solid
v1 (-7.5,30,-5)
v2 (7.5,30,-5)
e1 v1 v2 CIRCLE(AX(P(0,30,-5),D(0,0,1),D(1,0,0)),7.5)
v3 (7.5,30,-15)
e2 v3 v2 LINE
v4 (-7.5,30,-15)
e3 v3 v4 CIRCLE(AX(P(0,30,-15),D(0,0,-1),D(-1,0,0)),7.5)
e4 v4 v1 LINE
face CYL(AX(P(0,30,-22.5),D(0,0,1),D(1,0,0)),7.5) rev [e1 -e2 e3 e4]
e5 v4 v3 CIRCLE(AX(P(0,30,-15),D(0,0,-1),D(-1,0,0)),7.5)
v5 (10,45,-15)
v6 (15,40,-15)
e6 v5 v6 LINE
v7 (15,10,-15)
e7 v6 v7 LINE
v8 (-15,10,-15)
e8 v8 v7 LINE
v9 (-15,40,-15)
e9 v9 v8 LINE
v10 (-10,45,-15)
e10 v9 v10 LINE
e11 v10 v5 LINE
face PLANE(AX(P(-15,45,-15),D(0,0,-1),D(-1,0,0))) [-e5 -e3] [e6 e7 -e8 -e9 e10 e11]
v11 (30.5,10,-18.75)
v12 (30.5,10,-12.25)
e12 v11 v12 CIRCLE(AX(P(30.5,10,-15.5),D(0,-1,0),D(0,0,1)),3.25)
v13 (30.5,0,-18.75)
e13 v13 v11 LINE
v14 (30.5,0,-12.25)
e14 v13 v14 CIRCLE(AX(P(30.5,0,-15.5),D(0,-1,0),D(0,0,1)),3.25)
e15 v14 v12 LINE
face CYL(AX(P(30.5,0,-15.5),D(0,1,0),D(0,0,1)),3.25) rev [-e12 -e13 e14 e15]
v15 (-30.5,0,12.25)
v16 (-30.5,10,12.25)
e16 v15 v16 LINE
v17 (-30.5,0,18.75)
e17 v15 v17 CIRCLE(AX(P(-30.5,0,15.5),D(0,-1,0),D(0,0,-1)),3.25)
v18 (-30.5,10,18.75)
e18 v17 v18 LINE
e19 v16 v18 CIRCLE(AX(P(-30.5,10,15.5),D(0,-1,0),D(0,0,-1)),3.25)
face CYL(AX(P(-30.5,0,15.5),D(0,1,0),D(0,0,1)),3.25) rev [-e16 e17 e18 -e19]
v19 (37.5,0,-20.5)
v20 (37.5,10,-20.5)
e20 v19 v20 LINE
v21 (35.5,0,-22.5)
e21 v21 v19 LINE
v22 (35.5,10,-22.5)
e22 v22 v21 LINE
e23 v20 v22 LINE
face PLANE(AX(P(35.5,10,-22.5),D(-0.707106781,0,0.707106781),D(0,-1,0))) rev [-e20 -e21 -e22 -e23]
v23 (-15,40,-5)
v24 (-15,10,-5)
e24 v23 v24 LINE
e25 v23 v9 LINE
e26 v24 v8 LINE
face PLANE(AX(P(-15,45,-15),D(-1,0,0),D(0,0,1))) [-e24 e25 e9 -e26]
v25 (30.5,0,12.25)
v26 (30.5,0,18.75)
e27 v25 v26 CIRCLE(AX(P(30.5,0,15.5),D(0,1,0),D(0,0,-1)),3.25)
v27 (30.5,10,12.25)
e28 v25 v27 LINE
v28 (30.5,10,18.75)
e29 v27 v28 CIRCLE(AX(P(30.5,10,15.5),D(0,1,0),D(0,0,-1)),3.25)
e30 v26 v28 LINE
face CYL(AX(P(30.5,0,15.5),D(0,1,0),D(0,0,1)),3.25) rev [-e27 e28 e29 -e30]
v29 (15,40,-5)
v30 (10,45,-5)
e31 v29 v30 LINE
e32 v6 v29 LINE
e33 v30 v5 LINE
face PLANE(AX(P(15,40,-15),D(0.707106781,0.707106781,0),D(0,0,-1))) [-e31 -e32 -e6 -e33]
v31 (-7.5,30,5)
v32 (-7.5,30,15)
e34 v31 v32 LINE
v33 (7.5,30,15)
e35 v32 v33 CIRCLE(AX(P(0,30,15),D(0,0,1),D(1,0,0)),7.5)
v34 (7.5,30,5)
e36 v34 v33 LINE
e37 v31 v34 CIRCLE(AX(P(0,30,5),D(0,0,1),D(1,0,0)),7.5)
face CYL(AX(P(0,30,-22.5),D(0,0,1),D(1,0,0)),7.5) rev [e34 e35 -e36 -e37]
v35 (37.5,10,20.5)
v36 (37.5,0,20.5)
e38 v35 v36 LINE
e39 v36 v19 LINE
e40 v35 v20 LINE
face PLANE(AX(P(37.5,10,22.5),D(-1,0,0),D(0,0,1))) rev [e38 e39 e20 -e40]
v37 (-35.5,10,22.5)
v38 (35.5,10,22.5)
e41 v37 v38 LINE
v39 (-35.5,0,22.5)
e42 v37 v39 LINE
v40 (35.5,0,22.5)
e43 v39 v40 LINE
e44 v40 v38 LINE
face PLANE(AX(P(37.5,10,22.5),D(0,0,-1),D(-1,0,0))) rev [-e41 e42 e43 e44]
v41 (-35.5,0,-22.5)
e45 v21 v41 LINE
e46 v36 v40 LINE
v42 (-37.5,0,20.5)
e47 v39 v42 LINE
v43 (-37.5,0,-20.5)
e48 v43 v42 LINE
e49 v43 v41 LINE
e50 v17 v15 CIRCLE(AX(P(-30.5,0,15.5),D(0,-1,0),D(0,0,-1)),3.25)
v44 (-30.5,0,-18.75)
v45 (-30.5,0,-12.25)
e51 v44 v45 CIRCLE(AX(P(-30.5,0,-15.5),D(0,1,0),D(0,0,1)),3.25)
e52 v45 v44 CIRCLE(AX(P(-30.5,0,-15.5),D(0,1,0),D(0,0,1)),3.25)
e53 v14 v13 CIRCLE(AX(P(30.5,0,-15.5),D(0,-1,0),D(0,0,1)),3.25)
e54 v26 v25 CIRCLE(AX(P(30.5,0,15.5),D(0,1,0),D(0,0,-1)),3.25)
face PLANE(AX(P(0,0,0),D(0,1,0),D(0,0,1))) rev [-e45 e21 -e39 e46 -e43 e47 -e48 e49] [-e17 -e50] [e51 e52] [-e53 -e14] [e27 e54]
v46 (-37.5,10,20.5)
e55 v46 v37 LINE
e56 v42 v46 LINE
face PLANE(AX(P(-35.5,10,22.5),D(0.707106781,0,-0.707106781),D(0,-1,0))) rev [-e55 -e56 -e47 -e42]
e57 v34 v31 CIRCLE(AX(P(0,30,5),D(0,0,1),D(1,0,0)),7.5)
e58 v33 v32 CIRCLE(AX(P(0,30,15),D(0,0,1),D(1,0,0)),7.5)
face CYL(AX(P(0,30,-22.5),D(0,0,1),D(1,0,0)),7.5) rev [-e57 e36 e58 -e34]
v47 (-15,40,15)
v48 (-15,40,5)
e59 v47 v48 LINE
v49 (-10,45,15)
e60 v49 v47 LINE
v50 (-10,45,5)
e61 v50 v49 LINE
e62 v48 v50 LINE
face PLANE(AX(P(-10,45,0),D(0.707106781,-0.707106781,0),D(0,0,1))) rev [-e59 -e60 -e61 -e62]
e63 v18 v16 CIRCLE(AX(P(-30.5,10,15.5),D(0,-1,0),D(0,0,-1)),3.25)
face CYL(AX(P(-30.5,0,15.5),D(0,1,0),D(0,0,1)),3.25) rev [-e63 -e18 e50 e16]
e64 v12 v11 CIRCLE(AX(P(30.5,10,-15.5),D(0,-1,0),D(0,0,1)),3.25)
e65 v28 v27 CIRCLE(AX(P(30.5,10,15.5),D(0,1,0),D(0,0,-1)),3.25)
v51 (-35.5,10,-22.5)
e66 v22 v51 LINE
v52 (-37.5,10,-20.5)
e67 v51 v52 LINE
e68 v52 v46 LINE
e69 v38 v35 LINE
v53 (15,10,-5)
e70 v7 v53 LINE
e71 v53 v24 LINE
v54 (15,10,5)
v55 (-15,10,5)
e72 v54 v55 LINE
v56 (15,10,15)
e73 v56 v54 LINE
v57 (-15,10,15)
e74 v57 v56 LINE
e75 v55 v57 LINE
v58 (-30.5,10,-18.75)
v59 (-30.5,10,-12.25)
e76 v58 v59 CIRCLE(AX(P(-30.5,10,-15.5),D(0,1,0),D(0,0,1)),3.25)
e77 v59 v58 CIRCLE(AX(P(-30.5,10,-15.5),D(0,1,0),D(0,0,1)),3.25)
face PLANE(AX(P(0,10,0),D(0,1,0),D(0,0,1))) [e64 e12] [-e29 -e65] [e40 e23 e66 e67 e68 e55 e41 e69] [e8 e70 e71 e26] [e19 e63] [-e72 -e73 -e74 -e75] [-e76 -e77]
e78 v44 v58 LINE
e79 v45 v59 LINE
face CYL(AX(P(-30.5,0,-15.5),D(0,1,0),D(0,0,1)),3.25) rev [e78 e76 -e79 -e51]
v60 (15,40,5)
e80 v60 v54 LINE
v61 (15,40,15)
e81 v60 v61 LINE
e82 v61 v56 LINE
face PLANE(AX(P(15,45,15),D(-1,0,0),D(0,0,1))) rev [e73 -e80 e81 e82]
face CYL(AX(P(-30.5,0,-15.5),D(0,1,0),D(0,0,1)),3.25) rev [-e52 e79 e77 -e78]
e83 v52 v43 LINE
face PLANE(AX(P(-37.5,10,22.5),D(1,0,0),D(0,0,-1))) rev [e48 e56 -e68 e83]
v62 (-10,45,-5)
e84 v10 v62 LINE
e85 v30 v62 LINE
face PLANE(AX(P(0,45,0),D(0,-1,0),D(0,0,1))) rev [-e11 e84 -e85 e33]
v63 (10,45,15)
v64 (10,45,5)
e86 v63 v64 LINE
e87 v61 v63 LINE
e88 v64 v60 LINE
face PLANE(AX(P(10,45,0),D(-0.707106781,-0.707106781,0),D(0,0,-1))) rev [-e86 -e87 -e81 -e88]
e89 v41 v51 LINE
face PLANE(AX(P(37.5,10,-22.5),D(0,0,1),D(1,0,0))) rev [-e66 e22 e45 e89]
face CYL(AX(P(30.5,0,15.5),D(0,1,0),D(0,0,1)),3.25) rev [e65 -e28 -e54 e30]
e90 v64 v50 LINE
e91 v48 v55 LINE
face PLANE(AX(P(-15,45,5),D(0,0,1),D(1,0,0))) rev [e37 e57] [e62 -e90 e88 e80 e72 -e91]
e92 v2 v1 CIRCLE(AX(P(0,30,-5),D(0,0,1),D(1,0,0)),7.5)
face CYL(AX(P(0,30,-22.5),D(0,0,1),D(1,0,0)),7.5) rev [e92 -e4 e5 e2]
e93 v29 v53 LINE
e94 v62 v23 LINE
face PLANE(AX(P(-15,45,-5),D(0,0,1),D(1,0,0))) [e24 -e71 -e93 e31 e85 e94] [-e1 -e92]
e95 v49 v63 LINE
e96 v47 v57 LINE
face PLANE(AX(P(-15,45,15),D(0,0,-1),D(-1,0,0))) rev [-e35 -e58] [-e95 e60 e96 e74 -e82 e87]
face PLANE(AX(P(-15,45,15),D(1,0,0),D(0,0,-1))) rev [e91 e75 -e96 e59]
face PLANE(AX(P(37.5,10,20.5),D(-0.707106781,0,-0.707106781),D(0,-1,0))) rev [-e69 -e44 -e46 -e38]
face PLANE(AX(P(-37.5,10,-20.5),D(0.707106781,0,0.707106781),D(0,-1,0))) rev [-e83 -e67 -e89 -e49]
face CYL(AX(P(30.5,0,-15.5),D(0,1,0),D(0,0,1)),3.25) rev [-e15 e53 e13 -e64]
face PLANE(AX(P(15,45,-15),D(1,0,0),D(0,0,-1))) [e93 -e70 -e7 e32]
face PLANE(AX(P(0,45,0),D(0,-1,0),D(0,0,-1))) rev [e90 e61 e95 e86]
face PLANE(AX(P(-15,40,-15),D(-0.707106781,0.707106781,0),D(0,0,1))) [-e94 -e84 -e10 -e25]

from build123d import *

# Parameters (mm, degrees)
BASE_PLATE_SKETCH_W                        = 75
BASE_PLATE_SKETCH_H                        = 45
BASE_PLATE_75X45X10_DEPTH                  = 10
LUG_PROFILE_SKETCH_W                       = 30
LUG_PROFILE_SKETCH_H                       = 10
CLEVIS_LUG_DEPTH                           = 35
LUG_TOP_CHAMFERS_5MM_SIZE                  = 5
BASE_PLATE_EDGE_CHAMFER_2MM_SIZE           = 2
MOUNTING_HOLE_SKETCH_R                     = 3.25
MOUNTING_HOLE_6_5_DEPTH                    = 57.013391256
MOUNTING_HOLES_MIRROR_RIGHT_COPY_1_SKETC_R = 3.25
MOUNTING_HOLES_MIRROR_RIGHT_COPY_1_DEPTH   = 57.013391256
PIN_BORE_SKETCH_R                          = 7.5
PIN_BORE_15_DEPTH                          = 70.552138716


with BuildPart() as part:
    # Base Plate Sketch → Base Plate 75x45x10 (new body)
    with BuildSketch(Plane(origin=(0, 0, 0), x_dir=(1, 0, 0), z_dir=(0, 1, 0))):
        Rectangle(BASE_PLATE_SKETCH_W, BASE_PLATE_SKETCH_H)
    extrude(amount=BASE_PLATE_75X45X10_DEPTH)

    # Lug Profile Sketch → Clevis Lug (add)
    with BuildSketch(Plane(origin=(0, 10, 0), x_dir=(1, 0, 0), z_dir=(0, 1, 0))):
        with Locations((0, -10)):
            Rectangle(LUG_PROFILE_SKETCH_W, LUG_PROFILE_SKETCH_H)
    clevis_lug = extrude(amount=CLEVIS_LUG_DEPTH)

    # Clevis Lug Mirror: Clevis Lug across plane
    add(clevis_lug.mirror(Plane.XY))

    # Lug Top Chamfers 5mm
    lug_top_chamfers_5mm_edges = [part.edges().sort_by_distance(p)[0] for p in [
        (15, 45, 10),
        (-15, 45, 10),
        (15, 45, -10),
        (-15, 45, -10),
    ]]
    chamfer(lug_top_chamfers_5mm_edges, length=LUG_TOP_CHAMFERS_5MM_SIZE)

    # Base Plate Edge Chamfer 2mm
    base_plate_edge_chamfer_2mm_edges = [part.edges().sort_by_distance(p)[0] for p in [
        (-37.5, 5, -22.5),
        (37.5, 5, -22.5),
        (37.5, 5, 22.5),
        (-37.5, 5, 22.5),
    ]]
    chamfer(base_plate_edge_chamfer_2mm_edges, length=BASE_PLATE_EDGE_CHAMFER_2MM_SIZE)

    # Mounting Hole Sketch → Mounting Hole Ø6.5 (cut, through all)
    with BuildSketch(Plane(origin=(0, 10, 0), x_dir=(1, 0, 0), z_dir=(0, 1, 0))):
        with Locations(Location((-30.5, 15.5, 0), (0, 0, 270))):
            Circle(MOUNTING_HOLE_SKETCH_R)
    mounting_hole_6_5 = extrude(amount=-MOUNTING_HOLE_6_5_DEPTH, mode=Mode.SUBTRACT)

    # Mounting Hole Mirror Front: Mounting Hole Ø6.5 across plane
    add(mounting_hole_6_5.mirror(Plane.XY), mode=Mode.SUBTRACT)

    # Mounting Holes Mirror Right: Mounting Hole Ø6.5 across plane
    add(mounting_hole_6_5.mirror(Plane(origin=(0, 0, 0), x_dir=(0, 0, 1), z_dir=(1, 0, 0))), mode=Mode.SUBTRACT)

    # Mounting Holes Mirror Right copy 1 sketc → Mounting Holes Mirror Right copy 1 (cut, through all)
    with BuildSketch(Plane(origin=(0, 10, 0), x_dir=(-1, 0, 0), z_dir=(0, 1, 0))):
        with Locations(Location((-30.5, 15.5, 0), (0, 0, 270))):
            Circle(MOUNTING_HOLES_MIRROR_RIGHT_COPY_1_SKETC_R)
    extrude(amount=-MOUNTING_HOLES_MIRROR_RIGHT_COPY_1_DEPTH, mode=Mode.SUBTRACT)

    # Pin Bore Sketch → Pin Bore Ø15 (cut, through all)
    with BuildSketch(Plane.XY.offset(15)):
        with Locations((0, 30)):
            Circle(PIN_BORE_SKETCH_R)
    extrude(amount=-PIN_BORE_15_DEPTH, mode=Mode.SUBTRACT)


solid = part.part
